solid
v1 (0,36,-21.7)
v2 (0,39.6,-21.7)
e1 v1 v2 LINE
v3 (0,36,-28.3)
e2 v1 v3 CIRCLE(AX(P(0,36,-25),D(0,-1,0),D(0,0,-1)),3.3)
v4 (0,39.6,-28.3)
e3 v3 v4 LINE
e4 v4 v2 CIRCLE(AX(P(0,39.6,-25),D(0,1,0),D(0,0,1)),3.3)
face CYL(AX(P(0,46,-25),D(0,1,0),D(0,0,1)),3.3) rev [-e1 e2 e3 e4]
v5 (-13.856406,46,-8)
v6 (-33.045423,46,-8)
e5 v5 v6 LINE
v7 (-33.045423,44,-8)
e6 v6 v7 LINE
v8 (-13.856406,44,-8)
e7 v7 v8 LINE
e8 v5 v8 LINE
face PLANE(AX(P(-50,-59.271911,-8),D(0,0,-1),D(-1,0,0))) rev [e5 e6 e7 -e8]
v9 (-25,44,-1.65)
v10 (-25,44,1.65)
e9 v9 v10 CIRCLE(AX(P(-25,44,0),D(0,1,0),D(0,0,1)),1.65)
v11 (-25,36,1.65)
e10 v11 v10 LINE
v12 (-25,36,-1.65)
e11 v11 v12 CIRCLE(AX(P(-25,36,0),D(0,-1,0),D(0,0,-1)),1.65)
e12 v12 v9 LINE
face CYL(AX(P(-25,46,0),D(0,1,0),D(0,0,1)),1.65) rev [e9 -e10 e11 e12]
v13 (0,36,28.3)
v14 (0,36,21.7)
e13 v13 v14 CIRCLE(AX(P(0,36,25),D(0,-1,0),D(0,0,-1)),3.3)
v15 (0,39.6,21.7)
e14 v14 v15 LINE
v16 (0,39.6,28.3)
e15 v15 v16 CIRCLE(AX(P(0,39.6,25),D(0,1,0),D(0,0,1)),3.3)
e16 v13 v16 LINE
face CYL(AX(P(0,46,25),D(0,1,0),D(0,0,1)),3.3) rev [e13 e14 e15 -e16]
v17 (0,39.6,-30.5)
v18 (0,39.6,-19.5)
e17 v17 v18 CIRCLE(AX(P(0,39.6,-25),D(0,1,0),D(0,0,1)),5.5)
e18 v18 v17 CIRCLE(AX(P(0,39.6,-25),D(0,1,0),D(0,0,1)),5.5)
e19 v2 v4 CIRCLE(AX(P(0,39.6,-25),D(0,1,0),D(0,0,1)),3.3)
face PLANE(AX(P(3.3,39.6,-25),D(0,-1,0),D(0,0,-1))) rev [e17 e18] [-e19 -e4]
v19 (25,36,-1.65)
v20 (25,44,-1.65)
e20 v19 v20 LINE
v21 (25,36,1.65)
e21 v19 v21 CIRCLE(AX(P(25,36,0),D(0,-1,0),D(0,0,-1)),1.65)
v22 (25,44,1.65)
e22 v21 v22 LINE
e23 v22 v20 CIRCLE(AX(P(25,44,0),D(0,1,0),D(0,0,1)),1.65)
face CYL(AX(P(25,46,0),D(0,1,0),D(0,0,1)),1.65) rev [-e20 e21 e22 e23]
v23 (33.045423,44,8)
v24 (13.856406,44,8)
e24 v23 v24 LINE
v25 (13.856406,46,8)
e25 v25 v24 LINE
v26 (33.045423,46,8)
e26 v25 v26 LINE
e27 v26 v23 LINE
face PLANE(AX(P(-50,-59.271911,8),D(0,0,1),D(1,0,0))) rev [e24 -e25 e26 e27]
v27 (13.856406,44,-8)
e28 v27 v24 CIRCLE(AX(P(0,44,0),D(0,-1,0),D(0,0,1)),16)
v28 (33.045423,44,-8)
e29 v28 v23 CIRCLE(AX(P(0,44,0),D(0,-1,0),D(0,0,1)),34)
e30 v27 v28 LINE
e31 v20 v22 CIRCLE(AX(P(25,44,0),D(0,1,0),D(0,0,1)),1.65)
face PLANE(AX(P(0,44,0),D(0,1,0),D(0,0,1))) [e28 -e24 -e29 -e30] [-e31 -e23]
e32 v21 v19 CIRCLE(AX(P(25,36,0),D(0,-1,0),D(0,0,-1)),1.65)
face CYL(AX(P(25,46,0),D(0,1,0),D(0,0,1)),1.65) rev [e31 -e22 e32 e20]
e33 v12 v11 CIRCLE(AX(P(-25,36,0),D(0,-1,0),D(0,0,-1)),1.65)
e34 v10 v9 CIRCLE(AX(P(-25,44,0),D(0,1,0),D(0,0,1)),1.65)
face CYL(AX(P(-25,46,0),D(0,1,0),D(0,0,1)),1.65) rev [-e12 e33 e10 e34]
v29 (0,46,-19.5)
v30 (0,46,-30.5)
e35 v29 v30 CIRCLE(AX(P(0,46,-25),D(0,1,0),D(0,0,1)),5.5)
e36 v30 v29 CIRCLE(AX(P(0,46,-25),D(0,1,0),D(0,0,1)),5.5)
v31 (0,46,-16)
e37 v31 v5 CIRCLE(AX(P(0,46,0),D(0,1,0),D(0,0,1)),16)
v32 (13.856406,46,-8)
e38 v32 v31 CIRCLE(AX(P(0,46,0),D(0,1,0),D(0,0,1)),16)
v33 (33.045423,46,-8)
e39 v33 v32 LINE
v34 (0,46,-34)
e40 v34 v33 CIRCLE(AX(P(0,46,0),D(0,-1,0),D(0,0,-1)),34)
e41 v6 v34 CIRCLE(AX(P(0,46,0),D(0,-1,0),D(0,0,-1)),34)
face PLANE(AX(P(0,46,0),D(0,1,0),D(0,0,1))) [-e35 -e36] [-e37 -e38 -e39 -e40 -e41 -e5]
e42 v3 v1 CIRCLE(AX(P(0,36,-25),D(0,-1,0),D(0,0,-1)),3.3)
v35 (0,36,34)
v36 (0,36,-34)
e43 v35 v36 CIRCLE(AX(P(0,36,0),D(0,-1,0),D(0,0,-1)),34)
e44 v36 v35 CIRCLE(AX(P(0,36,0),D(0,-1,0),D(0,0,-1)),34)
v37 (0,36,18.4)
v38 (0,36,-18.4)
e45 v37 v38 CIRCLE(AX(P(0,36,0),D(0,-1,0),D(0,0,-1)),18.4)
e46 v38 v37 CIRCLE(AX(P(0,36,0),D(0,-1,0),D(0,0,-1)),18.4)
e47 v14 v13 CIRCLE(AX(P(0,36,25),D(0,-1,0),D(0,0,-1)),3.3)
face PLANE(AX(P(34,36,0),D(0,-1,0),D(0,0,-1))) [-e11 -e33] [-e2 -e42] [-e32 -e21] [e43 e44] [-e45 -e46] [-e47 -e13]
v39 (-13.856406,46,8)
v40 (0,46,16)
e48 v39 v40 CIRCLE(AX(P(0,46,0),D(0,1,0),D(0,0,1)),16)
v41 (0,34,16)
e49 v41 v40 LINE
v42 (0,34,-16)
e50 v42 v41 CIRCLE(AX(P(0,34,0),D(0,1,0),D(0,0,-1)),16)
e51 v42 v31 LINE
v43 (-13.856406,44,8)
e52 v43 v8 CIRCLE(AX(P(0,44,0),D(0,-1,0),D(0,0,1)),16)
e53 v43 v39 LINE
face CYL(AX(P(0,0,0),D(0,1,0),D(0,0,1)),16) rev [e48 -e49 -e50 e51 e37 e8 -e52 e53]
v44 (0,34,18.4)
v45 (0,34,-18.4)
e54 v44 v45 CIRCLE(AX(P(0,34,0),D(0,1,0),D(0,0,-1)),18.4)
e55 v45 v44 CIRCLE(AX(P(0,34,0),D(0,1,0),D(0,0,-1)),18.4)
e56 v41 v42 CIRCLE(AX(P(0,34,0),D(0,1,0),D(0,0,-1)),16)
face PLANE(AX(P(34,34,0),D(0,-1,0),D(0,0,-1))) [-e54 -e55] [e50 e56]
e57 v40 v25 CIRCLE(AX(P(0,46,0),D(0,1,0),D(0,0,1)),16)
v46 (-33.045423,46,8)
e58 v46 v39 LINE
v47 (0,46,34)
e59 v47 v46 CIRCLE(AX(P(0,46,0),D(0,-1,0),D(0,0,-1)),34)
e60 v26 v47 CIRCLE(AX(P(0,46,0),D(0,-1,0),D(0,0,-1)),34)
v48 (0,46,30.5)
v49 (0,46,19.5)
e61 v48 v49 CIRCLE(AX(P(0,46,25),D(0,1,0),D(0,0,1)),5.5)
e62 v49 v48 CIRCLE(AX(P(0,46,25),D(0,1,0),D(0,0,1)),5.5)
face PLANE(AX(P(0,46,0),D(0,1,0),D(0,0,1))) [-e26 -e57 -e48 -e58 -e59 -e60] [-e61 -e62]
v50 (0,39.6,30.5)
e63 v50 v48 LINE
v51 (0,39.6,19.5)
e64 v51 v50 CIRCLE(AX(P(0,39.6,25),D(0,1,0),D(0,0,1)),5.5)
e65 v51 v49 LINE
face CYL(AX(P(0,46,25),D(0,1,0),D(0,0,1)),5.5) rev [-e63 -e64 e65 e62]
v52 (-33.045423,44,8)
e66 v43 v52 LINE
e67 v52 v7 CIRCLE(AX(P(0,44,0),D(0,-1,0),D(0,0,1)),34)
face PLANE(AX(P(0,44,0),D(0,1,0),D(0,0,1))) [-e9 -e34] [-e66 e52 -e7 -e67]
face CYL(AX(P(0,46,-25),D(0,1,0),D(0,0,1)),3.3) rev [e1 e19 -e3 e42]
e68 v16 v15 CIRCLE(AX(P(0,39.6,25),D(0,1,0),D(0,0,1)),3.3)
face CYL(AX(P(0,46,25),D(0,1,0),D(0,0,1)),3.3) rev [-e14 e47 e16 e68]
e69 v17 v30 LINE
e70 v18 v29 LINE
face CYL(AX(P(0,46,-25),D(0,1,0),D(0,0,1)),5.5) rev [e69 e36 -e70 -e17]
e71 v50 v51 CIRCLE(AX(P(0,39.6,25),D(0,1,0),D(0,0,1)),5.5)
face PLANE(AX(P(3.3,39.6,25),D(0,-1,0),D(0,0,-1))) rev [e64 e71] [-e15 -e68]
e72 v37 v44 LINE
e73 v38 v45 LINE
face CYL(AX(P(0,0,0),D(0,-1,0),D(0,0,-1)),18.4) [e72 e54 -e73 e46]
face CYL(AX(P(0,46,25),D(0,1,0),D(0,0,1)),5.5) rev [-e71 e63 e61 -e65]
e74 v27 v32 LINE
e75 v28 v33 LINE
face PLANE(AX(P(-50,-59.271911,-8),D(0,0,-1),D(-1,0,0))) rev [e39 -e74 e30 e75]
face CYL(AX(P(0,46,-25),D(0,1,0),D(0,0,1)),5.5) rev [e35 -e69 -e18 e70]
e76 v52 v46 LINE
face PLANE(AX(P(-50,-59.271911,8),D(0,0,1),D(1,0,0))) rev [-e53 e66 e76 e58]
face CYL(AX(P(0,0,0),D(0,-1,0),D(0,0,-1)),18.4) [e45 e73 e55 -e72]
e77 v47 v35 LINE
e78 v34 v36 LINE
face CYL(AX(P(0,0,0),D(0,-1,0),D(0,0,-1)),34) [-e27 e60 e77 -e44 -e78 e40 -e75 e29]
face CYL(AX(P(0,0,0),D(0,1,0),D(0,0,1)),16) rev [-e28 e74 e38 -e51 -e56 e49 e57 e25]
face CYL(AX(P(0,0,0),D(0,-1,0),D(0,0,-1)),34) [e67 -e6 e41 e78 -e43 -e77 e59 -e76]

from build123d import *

# Parameters (mm, degrees)
HOLE_WIZARD_M6_1_D           = 6.6
HOLE_WIZARD_M6_1_CBORE_D     = 11
HOLE_WIZARD_M6_1_CBORE_DEPTH = 6.4
SKETCH_4_R                   = 16
CUT_EXTRUDE_1_DEPTH          = 67.543219038
EXTRUDE_1_DEPTH              = 10
SKETCH_6_W                   = 38
SKETCH_6_H                   = 16
CUT_EXTRUDE_2_DEPTH          = 10
CUT_EXTRUDE_3_DEPTH          = 74.810568349
CUT_EXTRUDE_3_DEPTH_BACK     = 74.810568349
SKETCH_7_R                   = 2
SKETCH_9_R                   = 20
CUT_EXTRUDE_5_DEPTH          = 34
SKETCH_10_W                  = 100
SKETCH_10_H                  = 16
CUT_EXTRUDE_6_DEPTH          = 12
HOLE_WIZARD_M4_1_D           = 3.3


with BuildPart() as part:
    # 草图1 → 旋转1 (revolve)
    with BuildSketch(Plane.XY, mode=Mode.PRIVATE) as revolve_1_sk:
        Polygon((0, 46), (34, 46), (34, 36), (18.4, 36), (18.4, 26), (17.492059993, 0), (0, 0), align=None)
    revolve(revolve_1_sk.sketch.rotate(Axis((0, 0, 0), (0, 1, 0)), 90), axis=Axis((0, 0, 0), (0, 1, 0)))

    # M6 六角凹头螺钉的柱形沉头孔1 (through all)
    with Locations(Plane(origin=(0, 46, 0), x_dir=(1, 0, 0), z_dir=(0, 1, 0))):
        with Locations((0, 25), (0, -25)):
            CounterBoreHole(HOLE_WIZARD_M6_1_D / 2, HOLE_WIZARD_M6_1_CBORE_D / 2, HOLE_WIZARD_M6_1_CBORE_DEPTH)

    # 草图4 → 切除-拉伸1 (cut, through all)
    with BuildSketch(Plane(origin=(0, 46, 0), x_dir=(1, 0, 0), z_dir=(0, 1, 0))):
        with Locations(Location((0, 0, 0), (0, 0, 270))):
            Circle(SKETCH_4_R)
    extrude(amount=-CUT_EXTRUDE_1_DEPTH, mode=Mode.SUBTRACT)

    # 草图5 → 凸台-拉伸1 (add)
    with BuildSketch(Plane(origin=(0, 46, 0), x_dir=(1, 0, 0), z_dir=(0, 1, 0))):
        with BuildLine():
            Line((33.045423284, -8), (13.856406461, -8))
            ThreePointArc((13.856406461, -8), (16, 0), (13.856406461, 8))
            Line((13.856406461, 8), (33.045423284, 8))
            ThreePointArc((33.045423284, 8), (34, 0), (33.045423284, -8))
        make_face()
        with BuildLine():
            Line((-33.045423284, 8), (-13.856406461, 8))
            ThreePointArc((-13.856406461, 8), (-16, 0), (-13.856406461, -8))
            Line((-13.856406461, -8), (-33.045423284, -8))
            ThreePointArc((-33.045423284, -8), (-34, 0), (-33.045423284, 8))
        make_face()
    extrude(amount=EXTRUDE_1_DEPTH)

    # 草图6 → 切除-拉伸2 (cut)
    with BuildSketch(Plane(origin=(0, 56, 0), x_dir=(1, 0, 0), z_dir=(0, 1, 0))):
        Rectangle(SKETCH_6_W, SKETCH_6_H)
    extrude(amount=-CUT_EXTRUDE_2_DEPTH, mode=Mode.SUBTRACT)

    # 草图7 → 切除-拉伸3 (cut, two sides: drawn at the far end of the back side and taken through both)
    with BuildSketch(Plane(origin=(0, 0, 0), x_dir=(0, 0, -1), z_dir=(1, 0, 0)).offset(-CUT_EXTRUDE_3_DEPTH_BACK)):
        with Locations((0, 50)):
            Circle(SKETCH_7_R)
    extrude(amount=CUT_EXTRUDE_3_DEPTH + CUT_EXTRUDE_3_DEPTH_BACK, mode=Mode.SUBTRACT)

    # 草图9 → 切除-拉伸5 (cut)
    with BuildSketch(Plane.XZ):
        Circle(SKETCH_9_R)
    extrude(amount=-CUT_EXTRUDE_5_DEPTH, mode=Mode.SUBTRACT)

    # 草图10 → 切除-拉伸6 (cut)
    with BuildSketch(Plane(origin=(0, 56, 0), x_dir=(1, 0, 0), z_dir=(0, 1, 0))):
        Rectangle(SKETCH_10_W, SKETCH_10_H)
    extrude(amount=-CUT_EXTRUDE_6_DEPTH, mode=Mode.SUBTRACT)

    # M4 螺纹孔1 (through all)
    with Locations(Plane(origin=(0, 46, 0), x_dir=(1, 0, 0), z_dir=(0, 1, 0))):
        with Locations((-25, 0), (25, 0)):
            Hole(HOLE_WIZARD_M4_1_D / 2)


solid = part.part
